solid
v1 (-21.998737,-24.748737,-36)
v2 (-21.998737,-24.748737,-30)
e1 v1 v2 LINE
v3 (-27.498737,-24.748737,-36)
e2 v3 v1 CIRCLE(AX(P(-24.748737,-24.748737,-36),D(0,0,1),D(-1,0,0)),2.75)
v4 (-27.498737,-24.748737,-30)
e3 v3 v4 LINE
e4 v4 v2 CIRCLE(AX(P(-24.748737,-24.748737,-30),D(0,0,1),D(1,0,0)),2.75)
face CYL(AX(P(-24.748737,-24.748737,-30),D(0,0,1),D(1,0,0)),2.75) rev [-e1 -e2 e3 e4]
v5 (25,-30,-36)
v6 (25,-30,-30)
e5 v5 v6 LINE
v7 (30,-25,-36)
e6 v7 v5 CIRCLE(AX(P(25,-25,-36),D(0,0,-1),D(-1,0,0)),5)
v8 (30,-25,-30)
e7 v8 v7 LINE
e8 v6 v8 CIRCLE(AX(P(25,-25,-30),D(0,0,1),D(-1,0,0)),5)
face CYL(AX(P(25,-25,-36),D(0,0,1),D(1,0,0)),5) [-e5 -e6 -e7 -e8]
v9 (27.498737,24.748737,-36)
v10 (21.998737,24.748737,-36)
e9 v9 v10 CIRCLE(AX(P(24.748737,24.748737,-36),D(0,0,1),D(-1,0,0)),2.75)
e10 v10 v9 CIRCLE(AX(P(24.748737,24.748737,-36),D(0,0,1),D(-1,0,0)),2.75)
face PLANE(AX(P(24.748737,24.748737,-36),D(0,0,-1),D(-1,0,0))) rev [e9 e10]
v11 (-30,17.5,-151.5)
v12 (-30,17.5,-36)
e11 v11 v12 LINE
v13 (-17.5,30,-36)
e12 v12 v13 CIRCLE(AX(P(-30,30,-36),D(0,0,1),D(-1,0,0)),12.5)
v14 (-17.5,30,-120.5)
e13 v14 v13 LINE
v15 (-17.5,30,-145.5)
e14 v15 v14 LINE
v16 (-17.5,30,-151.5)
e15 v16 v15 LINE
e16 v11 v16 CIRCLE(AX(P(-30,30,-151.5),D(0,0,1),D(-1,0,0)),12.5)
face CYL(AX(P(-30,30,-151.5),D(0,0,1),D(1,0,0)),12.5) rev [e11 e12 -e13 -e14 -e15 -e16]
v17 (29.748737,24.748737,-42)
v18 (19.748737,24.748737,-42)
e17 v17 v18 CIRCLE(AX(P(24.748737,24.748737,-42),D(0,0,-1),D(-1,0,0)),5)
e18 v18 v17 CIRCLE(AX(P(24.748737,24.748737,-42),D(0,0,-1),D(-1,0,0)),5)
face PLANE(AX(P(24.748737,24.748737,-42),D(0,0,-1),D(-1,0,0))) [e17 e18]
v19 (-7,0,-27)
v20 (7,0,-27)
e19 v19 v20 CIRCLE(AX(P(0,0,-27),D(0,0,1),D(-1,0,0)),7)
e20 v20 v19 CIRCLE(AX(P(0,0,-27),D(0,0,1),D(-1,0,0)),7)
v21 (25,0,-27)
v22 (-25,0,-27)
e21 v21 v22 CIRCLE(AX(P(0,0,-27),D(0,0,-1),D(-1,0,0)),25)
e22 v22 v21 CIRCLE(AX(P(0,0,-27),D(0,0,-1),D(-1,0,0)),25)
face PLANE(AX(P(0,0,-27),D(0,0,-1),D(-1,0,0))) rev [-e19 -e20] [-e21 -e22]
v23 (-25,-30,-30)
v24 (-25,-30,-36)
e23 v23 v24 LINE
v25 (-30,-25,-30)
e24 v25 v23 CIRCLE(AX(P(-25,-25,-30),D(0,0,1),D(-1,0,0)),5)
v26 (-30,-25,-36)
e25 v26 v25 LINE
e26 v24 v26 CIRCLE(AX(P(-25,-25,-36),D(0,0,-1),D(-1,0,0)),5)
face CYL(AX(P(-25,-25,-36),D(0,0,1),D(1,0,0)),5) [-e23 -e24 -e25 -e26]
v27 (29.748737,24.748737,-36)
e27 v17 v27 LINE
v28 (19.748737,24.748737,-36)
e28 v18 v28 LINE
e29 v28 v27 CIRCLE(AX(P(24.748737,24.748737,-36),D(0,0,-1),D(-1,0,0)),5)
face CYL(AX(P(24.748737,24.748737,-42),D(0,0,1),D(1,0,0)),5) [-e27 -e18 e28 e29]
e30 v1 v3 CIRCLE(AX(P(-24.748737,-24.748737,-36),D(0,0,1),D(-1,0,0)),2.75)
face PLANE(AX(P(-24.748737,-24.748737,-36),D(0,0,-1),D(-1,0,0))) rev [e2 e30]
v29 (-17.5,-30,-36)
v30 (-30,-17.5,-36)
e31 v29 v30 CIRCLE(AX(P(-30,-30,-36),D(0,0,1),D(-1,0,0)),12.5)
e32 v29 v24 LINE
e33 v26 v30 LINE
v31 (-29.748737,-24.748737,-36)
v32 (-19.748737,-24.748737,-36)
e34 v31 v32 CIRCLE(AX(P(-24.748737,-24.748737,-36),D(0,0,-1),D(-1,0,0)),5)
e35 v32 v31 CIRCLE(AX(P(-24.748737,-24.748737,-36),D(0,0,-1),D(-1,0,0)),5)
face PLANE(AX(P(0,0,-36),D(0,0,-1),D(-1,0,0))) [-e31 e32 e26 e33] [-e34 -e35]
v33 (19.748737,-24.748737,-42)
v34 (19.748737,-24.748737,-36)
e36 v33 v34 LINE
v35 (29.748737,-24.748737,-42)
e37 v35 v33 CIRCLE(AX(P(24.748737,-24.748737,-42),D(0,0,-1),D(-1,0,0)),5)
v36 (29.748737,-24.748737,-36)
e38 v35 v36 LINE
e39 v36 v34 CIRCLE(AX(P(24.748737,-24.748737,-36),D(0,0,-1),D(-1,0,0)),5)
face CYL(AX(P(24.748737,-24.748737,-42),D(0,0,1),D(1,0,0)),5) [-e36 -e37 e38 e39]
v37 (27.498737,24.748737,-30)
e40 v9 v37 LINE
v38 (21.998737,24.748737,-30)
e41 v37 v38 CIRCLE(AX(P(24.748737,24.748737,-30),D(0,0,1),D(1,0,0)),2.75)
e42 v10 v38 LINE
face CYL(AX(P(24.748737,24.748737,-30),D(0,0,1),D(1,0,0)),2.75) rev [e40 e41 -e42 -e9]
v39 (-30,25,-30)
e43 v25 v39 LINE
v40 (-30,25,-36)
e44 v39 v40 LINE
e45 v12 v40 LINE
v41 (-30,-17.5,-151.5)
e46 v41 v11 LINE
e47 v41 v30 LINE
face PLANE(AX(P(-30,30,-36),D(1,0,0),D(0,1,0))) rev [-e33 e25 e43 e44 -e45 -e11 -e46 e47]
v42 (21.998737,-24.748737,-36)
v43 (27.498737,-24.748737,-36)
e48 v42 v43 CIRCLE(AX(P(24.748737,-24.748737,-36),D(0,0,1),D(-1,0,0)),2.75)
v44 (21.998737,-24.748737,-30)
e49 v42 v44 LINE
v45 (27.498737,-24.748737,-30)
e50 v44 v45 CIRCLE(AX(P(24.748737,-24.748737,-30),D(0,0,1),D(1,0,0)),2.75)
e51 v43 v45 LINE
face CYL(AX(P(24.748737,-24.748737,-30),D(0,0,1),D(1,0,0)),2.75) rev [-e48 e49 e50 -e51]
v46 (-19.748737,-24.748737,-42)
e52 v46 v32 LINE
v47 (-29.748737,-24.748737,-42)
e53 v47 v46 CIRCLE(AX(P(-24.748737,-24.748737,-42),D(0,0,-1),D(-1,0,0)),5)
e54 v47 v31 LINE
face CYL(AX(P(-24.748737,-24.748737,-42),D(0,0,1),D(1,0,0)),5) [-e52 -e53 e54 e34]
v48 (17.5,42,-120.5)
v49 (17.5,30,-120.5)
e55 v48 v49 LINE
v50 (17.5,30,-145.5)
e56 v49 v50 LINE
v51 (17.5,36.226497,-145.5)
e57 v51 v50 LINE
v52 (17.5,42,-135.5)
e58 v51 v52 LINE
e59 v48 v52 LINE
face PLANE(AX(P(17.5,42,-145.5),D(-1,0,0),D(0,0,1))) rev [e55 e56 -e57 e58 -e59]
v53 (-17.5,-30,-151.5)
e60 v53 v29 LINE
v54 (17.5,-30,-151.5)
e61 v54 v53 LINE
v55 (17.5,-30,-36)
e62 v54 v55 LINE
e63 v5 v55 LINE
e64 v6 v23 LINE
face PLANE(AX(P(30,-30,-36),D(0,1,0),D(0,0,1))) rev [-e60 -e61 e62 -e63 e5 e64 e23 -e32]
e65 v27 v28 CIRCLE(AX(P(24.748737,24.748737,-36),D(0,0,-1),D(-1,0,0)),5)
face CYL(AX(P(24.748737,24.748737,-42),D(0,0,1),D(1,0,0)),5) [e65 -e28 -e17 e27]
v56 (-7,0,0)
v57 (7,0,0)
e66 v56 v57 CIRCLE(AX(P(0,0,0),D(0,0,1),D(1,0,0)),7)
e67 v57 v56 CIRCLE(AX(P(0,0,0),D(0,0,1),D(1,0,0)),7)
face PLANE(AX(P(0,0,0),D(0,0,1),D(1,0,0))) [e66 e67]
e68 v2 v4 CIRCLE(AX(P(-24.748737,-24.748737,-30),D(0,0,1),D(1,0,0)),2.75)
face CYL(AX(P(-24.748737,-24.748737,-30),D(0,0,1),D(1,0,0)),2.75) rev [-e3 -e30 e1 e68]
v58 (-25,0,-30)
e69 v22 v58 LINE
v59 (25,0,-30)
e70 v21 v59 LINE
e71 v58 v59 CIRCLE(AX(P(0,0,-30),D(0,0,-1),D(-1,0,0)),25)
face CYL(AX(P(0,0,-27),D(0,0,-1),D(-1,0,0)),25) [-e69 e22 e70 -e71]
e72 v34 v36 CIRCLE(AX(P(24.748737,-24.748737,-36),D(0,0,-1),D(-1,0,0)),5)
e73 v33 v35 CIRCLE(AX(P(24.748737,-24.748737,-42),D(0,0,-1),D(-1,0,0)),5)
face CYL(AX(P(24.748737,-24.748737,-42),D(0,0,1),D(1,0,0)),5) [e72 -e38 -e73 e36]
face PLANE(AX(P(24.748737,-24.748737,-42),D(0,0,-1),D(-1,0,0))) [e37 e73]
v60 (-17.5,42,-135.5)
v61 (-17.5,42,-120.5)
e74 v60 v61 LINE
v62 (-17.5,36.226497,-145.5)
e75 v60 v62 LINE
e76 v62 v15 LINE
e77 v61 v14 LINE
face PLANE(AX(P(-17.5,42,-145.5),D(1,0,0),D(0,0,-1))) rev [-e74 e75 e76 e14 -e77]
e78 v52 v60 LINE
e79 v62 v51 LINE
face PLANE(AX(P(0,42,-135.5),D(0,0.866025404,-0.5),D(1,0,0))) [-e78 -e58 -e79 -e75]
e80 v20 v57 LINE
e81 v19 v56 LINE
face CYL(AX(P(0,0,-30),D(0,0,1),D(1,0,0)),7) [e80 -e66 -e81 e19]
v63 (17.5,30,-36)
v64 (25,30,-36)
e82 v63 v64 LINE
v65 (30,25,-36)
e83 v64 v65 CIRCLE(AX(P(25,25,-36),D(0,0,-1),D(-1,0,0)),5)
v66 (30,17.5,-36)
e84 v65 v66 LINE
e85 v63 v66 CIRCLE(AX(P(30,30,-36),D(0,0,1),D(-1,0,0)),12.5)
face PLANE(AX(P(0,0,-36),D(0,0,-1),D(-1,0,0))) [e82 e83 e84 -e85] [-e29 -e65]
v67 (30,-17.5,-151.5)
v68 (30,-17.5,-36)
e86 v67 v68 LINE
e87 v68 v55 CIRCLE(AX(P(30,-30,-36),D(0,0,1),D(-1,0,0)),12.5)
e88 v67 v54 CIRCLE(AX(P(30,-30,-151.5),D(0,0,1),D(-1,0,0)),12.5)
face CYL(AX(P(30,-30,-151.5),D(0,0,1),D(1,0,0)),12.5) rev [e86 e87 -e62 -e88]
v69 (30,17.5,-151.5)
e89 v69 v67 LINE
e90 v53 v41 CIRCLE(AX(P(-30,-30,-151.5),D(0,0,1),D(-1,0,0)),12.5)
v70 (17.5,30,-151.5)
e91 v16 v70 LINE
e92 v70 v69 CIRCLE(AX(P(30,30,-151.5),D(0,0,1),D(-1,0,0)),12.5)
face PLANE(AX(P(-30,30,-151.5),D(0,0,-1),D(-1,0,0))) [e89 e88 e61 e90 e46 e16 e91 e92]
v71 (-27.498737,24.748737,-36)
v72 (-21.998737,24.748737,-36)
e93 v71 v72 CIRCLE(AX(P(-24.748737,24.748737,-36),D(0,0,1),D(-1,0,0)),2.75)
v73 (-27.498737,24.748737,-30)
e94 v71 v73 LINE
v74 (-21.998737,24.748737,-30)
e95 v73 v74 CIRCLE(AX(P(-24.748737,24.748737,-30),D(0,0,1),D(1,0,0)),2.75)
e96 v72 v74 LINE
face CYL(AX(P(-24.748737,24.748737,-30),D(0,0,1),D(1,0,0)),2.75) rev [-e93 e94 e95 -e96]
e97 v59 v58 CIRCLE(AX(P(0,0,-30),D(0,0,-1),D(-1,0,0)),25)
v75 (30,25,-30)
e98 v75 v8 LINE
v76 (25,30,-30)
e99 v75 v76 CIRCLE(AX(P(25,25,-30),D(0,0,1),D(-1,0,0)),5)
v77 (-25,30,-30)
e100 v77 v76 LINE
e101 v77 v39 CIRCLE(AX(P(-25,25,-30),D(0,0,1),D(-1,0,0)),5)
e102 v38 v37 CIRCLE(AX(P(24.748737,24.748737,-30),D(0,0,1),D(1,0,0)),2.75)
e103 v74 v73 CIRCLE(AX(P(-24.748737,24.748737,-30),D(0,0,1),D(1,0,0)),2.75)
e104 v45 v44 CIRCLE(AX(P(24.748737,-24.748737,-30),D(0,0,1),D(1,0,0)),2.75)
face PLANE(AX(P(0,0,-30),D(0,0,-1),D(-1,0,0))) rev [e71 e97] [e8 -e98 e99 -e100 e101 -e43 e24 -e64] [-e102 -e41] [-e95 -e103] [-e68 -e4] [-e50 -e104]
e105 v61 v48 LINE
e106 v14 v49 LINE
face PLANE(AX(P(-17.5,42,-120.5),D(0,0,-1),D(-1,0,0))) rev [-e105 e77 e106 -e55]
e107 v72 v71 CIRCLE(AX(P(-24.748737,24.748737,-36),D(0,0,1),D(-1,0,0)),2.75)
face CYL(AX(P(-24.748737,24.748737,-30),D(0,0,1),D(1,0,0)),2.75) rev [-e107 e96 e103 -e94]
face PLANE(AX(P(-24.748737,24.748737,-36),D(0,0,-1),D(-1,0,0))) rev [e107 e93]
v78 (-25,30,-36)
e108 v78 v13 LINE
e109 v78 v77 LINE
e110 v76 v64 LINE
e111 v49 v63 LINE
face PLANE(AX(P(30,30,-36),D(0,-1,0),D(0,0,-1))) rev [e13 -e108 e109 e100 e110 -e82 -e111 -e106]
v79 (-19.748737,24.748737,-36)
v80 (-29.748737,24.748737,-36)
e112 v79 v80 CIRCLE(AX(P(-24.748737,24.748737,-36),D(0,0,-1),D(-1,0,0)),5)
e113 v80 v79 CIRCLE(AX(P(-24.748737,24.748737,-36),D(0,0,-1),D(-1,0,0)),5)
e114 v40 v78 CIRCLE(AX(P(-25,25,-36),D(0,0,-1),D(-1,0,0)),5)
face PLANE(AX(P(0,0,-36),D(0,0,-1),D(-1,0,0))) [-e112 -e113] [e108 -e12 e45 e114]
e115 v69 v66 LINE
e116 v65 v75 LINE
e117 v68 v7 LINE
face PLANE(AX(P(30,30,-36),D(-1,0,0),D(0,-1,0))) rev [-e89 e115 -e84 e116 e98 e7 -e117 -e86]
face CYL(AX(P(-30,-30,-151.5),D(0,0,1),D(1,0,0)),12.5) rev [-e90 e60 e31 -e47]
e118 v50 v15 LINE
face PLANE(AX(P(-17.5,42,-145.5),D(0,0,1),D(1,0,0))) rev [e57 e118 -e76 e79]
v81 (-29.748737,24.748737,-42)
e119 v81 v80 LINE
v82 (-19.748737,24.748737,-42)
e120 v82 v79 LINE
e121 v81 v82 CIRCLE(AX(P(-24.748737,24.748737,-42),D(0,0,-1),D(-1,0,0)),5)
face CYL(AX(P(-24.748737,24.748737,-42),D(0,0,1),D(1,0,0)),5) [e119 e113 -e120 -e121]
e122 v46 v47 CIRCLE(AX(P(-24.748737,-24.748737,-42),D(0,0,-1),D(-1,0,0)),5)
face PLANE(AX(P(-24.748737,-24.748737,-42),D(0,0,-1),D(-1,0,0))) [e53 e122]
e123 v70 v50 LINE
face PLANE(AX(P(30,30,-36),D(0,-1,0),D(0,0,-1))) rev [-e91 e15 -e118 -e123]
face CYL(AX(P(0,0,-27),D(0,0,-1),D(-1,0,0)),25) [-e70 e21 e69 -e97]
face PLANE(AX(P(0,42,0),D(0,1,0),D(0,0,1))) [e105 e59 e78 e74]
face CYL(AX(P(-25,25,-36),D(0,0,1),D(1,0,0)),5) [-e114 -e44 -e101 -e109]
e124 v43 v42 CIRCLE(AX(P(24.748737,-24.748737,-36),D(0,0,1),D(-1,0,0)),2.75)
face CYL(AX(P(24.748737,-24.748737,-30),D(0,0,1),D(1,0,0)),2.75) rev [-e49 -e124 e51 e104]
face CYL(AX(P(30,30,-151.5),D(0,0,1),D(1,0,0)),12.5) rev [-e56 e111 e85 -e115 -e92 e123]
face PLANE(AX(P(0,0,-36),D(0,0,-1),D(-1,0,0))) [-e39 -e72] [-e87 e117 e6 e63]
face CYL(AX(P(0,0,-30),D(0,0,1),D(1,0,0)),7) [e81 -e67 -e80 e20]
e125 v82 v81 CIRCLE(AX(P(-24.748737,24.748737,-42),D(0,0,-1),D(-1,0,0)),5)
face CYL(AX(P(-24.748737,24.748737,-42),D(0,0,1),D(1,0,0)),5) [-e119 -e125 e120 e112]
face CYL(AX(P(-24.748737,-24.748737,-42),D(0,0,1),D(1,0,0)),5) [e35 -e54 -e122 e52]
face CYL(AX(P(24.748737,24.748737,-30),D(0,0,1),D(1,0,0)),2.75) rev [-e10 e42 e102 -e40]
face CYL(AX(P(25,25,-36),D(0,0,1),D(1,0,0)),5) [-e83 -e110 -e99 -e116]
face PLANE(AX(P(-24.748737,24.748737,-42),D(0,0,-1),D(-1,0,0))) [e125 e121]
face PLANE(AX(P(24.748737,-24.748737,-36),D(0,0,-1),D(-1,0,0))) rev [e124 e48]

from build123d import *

# Parameters (mm, degrees)
SKETCH1_R                      = 7
BOSS_EXTRUDE1_DEPTH            = 30
SKETCH2_R                      = 25
BOSS_EXTRUDE2_DEPTH            = 3
SKETCH3_W                      = 60
SKETCH3_H                      = 60
BOSS_EXTRUDE3_DEPTH            = 6
BOSS_EXTRUDE4_DEPTH            = 115.5
SKETCH5_W                      = 35
SKETCH5_H                      = 25
BOSS_EXTRUDE5_DEPTH            = 12
CHAMFER1_SIZE                  = 10
CHAMFER1_SIZE2                 = 5.773502692
F_5_5_5_5_DIAMETER_HOLE1_D     = 5.5
F_5_5_5_5_DIAMETER_HOLE1_DEPTH = 20
F_5_5_5_5_DIAMETER_HOLE1_TIP   = 1.652366702
FILLET1_R                      = 5
SKETCH8_R                      = 5
BOSS_EXTRUDE6_DEPTH            = 6


with BuildPart() as part:
    # Sketch1 → Boss-Extrude1 (new body)
    with BuildSketch(Plane.XY):
        Circle(SKETCH1_R)
    extrude(amount=-BOSS_EXTRUDE1_DEPTH)

    # Sketch2 → Boss-Extrude2 (add)
    with BuildSketch(Plane(origin=(0, 0, -30), x_dir=(-1, 0, 0), z_dir=(0, 0, -1))):
        Circle(SKETCH2_R)
    extrude(amount=-BOSS_EXTRUDE2_DEPTH)

    # Sketch3 → Boss-Extrude3 (add)
    with BuildSketch(Plane(origin=(0, 0, -30), x_dir=(-1, 0, 0), z_dir=(0, 0, -1))):
        Rectangle(SKETCH3_W, SKETCH3_H)
    extrude(amount=BOSS_EXTRUDE3_DEPTH)

    # Sketch4 → Boss-Extrude4 (add)
    with BuildSketch(Plane(origin=(0, 0, -36), x_dir=(-1, 0, 0), z_dir=(0, 0, -1))):
        with BuildLine():
            Line((30, -17.5), (30, 17.5))
            ThreePointArc((30, 17.5), (21.161165235, 21.161165235), (17.5, 30))
            Line((17.5, 30), (-17.5, 30))
            ThreePointArc((-17.5, 30), (-21.161165235, 21.161165235), (-30, 17.5))
            Line((-30, 17.5), (-30, -17.5))
            ThreePointArc((-30, -17.5), (-21.161165235, -21.161165235), (-17.5, -30))
            Line((-17.5, -30), (17.5, -30))
            ThreePointArc((17.5, -30), (21.161165235, -21.161165235), (30, -17.5))
        make_face()
    extrude(amount=BOSS_EXTRUDE4_DEPTH)

    # Sketch5 → Boss-Extrude5 (add)
    with BuildSketch(Plane(origin=(0, 30, 0), x_dir=(1, 0, 0), z_dir=(0, 1, 0))):
        with Locations((0, 133)):
            Rectangle(SKETCH5_W, SKETCH5_H)
    extrude(amount=BOSS_EXTRUDE5_DEPTH)

    # Chamfer1
    chamfer1_edges = [part.edges().sort_by_distance(p)[0] for p in [
        (0, 42, -145.5),
    ]]
    chamfer1_side = [part.faces().sort_by_distance(p)[0] for p in [
        (0, 42, -133),
    ]]
    chamfer(chamfer1_edges, length=CHAMFER1_SIZE, length2=CHAMFER1_SIZE2, reference=chamfer1_side[0])

    # Ø5.5 (5.5) Diameter Hole1
    with Locations(Plane.XY.offset(-30)):
        with Locations((24.748737342, 24.748737342), (-24.748737342, 24.748737342), (24.748737342, -24.748737342), (-24.748737342, -24.748737342)):
            Hole(F_5_5_5_5_DIAMETER_HOLE1_D / 2, depth=F_5_5_5_5_DIAMETER_HOLE1_DEPTH)
            with Locations((0, 0, -(F_5_5_5_5_DIAMETER_HOLE1_DEPTH + F_5_5_5_5_DIAMETER_HOLE1_TIP / 2))):  # 118° drill point
                Cone(0, F_5_5_5_5_DIAMETER_HOLE1_D / 2, F_5_5_5_5_DIAMETER_HOLE1_TIP, mode=Mode.SUBTRACT)

    # Fillet1
    fillet1_edges = [part.edges().sort_by_distance(p)[0] for p in [
        (30, -30, -33),
        (-30, -30, -33),
        (-30, 30, -33),
        (30, 30, -33),
    ]]
    fillet(fillet1_edges, radius=FILLET1_R)

    # Sketch8 → Boss-Extrude6 (add)
    with BuildSketch(Plane(origin=(0, 0, -36), x_dir=(-1, 0, 0), z_dir=(0, 0, -1))):
        with Locations((-24.748737342, 24.748737342)):
            Circle(SKETCH8_R)
        with Locations((-24.748737342, -24.748737342)):
            Circle(SKETCH8_R)
        with Locations((24.748737342, -24.748737342)):
            Circle(SKETCH8_R)
        with Locations((24.748737342, 24.748737342)):
            Circle(SKETCH8_R)
    extrude(amount=BOSS_EXTRUDE6_DEPTH)


solid = part.part
